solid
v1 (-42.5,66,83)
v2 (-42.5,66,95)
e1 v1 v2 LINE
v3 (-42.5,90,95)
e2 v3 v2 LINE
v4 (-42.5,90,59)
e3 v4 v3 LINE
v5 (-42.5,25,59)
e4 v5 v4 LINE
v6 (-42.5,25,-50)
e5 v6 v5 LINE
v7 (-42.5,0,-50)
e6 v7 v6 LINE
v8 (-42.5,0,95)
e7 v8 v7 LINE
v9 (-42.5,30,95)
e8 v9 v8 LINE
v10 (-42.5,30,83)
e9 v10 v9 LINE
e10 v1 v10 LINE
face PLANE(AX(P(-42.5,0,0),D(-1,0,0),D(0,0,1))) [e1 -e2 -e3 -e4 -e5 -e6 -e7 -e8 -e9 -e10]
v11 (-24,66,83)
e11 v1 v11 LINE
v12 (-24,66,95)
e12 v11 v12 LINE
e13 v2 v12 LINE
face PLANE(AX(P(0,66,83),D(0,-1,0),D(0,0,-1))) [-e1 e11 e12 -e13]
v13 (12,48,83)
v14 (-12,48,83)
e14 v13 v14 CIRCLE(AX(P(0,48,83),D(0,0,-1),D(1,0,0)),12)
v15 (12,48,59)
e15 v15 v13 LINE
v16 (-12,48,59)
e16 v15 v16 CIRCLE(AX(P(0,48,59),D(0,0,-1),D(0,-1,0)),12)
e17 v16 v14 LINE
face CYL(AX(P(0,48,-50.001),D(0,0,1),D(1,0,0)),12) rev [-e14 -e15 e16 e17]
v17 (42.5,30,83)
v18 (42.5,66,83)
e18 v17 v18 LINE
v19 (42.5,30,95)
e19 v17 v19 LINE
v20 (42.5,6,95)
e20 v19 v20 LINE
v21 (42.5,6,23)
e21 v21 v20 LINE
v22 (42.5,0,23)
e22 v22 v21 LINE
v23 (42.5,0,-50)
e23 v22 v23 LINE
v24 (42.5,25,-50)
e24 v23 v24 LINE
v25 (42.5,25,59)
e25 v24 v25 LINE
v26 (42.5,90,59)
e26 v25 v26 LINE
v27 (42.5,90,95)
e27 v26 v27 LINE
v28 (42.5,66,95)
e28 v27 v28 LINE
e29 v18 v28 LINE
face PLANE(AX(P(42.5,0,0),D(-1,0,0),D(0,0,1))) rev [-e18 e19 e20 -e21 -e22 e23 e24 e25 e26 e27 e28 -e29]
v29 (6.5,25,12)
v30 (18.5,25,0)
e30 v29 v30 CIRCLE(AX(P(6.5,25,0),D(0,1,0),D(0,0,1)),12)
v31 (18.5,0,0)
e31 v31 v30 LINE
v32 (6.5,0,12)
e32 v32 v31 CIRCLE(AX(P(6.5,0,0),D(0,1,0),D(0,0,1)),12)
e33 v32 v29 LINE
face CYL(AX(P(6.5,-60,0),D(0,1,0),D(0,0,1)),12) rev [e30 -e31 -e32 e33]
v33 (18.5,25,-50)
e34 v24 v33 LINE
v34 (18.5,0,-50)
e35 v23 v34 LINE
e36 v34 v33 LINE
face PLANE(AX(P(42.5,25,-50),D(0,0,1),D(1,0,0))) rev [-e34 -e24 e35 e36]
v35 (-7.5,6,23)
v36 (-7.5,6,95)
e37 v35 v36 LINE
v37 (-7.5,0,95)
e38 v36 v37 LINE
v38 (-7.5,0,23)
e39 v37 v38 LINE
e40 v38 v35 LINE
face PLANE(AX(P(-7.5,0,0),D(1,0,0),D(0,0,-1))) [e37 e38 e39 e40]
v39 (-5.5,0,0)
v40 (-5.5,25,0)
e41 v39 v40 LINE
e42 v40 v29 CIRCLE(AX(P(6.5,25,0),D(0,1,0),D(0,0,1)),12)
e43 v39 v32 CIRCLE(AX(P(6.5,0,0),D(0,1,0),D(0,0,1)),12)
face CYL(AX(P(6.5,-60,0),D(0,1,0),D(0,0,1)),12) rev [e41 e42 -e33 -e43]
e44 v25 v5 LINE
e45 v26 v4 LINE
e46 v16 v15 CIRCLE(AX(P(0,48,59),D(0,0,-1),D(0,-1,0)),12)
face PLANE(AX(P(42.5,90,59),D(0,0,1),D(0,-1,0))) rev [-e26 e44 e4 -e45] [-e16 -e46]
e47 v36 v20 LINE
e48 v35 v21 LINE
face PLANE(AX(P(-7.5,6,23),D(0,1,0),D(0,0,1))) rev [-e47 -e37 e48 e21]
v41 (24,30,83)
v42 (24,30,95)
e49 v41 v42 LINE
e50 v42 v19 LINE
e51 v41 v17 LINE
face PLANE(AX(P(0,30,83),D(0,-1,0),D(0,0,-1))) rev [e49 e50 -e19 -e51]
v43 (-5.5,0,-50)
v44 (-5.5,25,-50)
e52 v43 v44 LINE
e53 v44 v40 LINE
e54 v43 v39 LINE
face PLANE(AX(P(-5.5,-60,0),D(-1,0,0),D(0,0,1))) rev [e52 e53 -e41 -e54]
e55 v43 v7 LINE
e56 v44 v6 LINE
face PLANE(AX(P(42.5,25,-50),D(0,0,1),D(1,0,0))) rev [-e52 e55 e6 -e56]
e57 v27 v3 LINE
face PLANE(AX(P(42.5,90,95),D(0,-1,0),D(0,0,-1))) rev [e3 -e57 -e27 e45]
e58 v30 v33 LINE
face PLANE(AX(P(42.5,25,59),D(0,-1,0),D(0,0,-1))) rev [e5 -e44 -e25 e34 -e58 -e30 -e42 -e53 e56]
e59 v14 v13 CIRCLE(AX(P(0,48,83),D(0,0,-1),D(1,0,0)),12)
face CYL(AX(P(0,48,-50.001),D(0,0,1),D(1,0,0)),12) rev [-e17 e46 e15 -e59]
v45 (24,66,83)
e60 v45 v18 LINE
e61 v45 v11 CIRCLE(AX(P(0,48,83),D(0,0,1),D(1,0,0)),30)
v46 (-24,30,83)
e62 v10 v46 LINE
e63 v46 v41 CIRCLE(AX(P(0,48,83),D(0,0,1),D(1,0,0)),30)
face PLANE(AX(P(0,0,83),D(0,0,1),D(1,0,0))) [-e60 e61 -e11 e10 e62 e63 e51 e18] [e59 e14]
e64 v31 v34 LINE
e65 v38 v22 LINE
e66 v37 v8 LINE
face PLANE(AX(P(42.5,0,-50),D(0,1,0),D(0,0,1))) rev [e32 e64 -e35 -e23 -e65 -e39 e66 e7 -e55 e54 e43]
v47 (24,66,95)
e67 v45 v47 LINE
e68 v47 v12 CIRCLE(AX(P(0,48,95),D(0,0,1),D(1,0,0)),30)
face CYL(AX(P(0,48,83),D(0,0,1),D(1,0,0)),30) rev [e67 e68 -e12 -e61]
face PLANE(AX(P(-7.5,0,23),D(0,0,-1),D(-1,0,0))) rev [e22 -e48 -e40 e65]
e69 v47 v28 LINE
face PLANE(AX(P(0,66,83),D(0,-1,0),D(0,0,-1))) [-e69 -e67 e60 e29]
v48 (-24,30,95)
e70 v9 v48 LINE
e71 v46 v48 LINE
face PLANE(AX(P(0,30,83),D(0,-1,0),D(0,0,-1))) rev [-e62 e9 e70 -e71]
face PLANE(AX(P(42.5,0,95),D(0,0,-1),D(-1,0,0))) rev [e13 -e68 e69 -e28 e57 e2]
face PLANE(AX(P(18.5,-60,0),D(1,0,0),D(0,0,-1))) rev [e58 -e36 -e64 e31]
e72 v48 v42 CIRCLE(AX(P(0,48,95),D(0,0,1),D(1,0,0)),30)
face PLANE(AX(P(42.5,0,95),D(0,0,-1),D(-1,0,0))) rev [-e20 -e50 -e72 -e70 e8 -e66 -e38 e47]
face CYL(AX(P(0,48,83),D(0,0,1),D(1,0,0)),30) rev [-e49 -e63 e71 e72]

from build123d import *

# Parameters (mm, degrees)
FORKED_BLOCK_BODY_DEPTH      = 42.5
SLOT_12X24_DEPTH             = 85
RELIEF_GROOVE_SKETCH_W       = 72
RELIEF_GROOVE_SKETCH_H       = 6
BOTTOM_RELIEF_GROOVE_6_DEPTH = 50
BORE_AND_SADDLE_SKETCH_R     = 12
SADDLE_RECESS_48_DEPTH       = 12
BORE_24_REACH                = 177.873
SKETCH6_3_R                  = 12


with BuildPart() as part:
    # Block Profile Sketch → Forked Block Body (new, symmetric)
    with BuildSketch(Plane(origin=(0, 0, 0), x_dir=(0, 0, -1), z_dir=(1, 0, 0))):
        Polygon((50, 0), (-95, 0), (-95, 90), (-59, 90), (-59, 25), (50, 25), align=None)
    extrude(amount=FORKED_BLOCK_BODY_DEPTH, both=True)

    # Slot Sketch → Slot 12x24 (cut)
    with BuildSketch(Plane(origin=(0, 25, 0), x_dir=(1, 0, 0), z_dir=(0, 1, 0))):
        with BuildLine():
            Line((18.5, 0), (18.5, 50))
            Line((18.5, 50), (-5.5, 50))
            Line((-5.5, 50), (-5.5, 0))
            ThreePointArc((-5.5, 0), (6.5, -12), (18.5, 0))
        make_face()
    extrude(amount=-SLOT_12X24_DEPTH, mode=Mode.SUBTRACT)

    # Relief Groove Sketch → Bottom Relief Groove 6 (cut)
    with BuildSketch(Plane(origin=(42.5, 0, 0), x_dir=(0, 0, -1), z_dir=(1, 0, 0))):
        with Locations((-59, 3)):
            Rectangle(RELIEF_GROOVE_SKETCH_W, RELIEF_GROOVE_SKETCH_H)
    extrude(amount=-BOTTOM_RELIEF_GROOVE_6_DEPTH, mode=Mode.SUBTRACT)

    # Bore and Saddle Sketch → Saddle Recess _48 (cut)
    with BuildSketch(Plane.XY.offset(95)):
        with BuildLine():
            Line((-42.5, 66), (-42.5, 30))
            Line((-42.5, 30), (-24, 30))
            ThreePointArc((-24, 30), (0, 18), (24, 30))
            Line((24, 30), (42.5, 30))
            Line((42.5, 30), (42.5, 66))
            Line((42.5, 66), (24, 66))
            ThreePointArc((24, 66), (0, 78), (-24, 66))
            Line((-24, 66), (-42.5, 66))
        make_face()
        with Locations((0, 48)):
            Circle(BORE_AND_SADDLE_SKETCH_R, mode=Mode.SUBTRACT)
    extrude(amount=-SADDLE_RECESS_48_DEPTH, mode=Mode.SUBTRACT)

    # Sketch6_3 → Bore _24 (cut, up to next)
    with BuildSketch(Plane.XY.offset(95), mode=Mode.PRIVATE) as bore_24_sk1:
        with Locations((0, 48)):
            Circle(SKETCH6_3_R)
    bore_24_tool1 = extrude(bore_24_sk1.sketch, amount=-BORE_24_REACH, mode=Mode.PRIVATE) & part.part
    add(bore_24_tool1.solids().sort_by_distance((0, 48, 95))[0], mode=Mode.SUBTRACT)


solid = part.part
